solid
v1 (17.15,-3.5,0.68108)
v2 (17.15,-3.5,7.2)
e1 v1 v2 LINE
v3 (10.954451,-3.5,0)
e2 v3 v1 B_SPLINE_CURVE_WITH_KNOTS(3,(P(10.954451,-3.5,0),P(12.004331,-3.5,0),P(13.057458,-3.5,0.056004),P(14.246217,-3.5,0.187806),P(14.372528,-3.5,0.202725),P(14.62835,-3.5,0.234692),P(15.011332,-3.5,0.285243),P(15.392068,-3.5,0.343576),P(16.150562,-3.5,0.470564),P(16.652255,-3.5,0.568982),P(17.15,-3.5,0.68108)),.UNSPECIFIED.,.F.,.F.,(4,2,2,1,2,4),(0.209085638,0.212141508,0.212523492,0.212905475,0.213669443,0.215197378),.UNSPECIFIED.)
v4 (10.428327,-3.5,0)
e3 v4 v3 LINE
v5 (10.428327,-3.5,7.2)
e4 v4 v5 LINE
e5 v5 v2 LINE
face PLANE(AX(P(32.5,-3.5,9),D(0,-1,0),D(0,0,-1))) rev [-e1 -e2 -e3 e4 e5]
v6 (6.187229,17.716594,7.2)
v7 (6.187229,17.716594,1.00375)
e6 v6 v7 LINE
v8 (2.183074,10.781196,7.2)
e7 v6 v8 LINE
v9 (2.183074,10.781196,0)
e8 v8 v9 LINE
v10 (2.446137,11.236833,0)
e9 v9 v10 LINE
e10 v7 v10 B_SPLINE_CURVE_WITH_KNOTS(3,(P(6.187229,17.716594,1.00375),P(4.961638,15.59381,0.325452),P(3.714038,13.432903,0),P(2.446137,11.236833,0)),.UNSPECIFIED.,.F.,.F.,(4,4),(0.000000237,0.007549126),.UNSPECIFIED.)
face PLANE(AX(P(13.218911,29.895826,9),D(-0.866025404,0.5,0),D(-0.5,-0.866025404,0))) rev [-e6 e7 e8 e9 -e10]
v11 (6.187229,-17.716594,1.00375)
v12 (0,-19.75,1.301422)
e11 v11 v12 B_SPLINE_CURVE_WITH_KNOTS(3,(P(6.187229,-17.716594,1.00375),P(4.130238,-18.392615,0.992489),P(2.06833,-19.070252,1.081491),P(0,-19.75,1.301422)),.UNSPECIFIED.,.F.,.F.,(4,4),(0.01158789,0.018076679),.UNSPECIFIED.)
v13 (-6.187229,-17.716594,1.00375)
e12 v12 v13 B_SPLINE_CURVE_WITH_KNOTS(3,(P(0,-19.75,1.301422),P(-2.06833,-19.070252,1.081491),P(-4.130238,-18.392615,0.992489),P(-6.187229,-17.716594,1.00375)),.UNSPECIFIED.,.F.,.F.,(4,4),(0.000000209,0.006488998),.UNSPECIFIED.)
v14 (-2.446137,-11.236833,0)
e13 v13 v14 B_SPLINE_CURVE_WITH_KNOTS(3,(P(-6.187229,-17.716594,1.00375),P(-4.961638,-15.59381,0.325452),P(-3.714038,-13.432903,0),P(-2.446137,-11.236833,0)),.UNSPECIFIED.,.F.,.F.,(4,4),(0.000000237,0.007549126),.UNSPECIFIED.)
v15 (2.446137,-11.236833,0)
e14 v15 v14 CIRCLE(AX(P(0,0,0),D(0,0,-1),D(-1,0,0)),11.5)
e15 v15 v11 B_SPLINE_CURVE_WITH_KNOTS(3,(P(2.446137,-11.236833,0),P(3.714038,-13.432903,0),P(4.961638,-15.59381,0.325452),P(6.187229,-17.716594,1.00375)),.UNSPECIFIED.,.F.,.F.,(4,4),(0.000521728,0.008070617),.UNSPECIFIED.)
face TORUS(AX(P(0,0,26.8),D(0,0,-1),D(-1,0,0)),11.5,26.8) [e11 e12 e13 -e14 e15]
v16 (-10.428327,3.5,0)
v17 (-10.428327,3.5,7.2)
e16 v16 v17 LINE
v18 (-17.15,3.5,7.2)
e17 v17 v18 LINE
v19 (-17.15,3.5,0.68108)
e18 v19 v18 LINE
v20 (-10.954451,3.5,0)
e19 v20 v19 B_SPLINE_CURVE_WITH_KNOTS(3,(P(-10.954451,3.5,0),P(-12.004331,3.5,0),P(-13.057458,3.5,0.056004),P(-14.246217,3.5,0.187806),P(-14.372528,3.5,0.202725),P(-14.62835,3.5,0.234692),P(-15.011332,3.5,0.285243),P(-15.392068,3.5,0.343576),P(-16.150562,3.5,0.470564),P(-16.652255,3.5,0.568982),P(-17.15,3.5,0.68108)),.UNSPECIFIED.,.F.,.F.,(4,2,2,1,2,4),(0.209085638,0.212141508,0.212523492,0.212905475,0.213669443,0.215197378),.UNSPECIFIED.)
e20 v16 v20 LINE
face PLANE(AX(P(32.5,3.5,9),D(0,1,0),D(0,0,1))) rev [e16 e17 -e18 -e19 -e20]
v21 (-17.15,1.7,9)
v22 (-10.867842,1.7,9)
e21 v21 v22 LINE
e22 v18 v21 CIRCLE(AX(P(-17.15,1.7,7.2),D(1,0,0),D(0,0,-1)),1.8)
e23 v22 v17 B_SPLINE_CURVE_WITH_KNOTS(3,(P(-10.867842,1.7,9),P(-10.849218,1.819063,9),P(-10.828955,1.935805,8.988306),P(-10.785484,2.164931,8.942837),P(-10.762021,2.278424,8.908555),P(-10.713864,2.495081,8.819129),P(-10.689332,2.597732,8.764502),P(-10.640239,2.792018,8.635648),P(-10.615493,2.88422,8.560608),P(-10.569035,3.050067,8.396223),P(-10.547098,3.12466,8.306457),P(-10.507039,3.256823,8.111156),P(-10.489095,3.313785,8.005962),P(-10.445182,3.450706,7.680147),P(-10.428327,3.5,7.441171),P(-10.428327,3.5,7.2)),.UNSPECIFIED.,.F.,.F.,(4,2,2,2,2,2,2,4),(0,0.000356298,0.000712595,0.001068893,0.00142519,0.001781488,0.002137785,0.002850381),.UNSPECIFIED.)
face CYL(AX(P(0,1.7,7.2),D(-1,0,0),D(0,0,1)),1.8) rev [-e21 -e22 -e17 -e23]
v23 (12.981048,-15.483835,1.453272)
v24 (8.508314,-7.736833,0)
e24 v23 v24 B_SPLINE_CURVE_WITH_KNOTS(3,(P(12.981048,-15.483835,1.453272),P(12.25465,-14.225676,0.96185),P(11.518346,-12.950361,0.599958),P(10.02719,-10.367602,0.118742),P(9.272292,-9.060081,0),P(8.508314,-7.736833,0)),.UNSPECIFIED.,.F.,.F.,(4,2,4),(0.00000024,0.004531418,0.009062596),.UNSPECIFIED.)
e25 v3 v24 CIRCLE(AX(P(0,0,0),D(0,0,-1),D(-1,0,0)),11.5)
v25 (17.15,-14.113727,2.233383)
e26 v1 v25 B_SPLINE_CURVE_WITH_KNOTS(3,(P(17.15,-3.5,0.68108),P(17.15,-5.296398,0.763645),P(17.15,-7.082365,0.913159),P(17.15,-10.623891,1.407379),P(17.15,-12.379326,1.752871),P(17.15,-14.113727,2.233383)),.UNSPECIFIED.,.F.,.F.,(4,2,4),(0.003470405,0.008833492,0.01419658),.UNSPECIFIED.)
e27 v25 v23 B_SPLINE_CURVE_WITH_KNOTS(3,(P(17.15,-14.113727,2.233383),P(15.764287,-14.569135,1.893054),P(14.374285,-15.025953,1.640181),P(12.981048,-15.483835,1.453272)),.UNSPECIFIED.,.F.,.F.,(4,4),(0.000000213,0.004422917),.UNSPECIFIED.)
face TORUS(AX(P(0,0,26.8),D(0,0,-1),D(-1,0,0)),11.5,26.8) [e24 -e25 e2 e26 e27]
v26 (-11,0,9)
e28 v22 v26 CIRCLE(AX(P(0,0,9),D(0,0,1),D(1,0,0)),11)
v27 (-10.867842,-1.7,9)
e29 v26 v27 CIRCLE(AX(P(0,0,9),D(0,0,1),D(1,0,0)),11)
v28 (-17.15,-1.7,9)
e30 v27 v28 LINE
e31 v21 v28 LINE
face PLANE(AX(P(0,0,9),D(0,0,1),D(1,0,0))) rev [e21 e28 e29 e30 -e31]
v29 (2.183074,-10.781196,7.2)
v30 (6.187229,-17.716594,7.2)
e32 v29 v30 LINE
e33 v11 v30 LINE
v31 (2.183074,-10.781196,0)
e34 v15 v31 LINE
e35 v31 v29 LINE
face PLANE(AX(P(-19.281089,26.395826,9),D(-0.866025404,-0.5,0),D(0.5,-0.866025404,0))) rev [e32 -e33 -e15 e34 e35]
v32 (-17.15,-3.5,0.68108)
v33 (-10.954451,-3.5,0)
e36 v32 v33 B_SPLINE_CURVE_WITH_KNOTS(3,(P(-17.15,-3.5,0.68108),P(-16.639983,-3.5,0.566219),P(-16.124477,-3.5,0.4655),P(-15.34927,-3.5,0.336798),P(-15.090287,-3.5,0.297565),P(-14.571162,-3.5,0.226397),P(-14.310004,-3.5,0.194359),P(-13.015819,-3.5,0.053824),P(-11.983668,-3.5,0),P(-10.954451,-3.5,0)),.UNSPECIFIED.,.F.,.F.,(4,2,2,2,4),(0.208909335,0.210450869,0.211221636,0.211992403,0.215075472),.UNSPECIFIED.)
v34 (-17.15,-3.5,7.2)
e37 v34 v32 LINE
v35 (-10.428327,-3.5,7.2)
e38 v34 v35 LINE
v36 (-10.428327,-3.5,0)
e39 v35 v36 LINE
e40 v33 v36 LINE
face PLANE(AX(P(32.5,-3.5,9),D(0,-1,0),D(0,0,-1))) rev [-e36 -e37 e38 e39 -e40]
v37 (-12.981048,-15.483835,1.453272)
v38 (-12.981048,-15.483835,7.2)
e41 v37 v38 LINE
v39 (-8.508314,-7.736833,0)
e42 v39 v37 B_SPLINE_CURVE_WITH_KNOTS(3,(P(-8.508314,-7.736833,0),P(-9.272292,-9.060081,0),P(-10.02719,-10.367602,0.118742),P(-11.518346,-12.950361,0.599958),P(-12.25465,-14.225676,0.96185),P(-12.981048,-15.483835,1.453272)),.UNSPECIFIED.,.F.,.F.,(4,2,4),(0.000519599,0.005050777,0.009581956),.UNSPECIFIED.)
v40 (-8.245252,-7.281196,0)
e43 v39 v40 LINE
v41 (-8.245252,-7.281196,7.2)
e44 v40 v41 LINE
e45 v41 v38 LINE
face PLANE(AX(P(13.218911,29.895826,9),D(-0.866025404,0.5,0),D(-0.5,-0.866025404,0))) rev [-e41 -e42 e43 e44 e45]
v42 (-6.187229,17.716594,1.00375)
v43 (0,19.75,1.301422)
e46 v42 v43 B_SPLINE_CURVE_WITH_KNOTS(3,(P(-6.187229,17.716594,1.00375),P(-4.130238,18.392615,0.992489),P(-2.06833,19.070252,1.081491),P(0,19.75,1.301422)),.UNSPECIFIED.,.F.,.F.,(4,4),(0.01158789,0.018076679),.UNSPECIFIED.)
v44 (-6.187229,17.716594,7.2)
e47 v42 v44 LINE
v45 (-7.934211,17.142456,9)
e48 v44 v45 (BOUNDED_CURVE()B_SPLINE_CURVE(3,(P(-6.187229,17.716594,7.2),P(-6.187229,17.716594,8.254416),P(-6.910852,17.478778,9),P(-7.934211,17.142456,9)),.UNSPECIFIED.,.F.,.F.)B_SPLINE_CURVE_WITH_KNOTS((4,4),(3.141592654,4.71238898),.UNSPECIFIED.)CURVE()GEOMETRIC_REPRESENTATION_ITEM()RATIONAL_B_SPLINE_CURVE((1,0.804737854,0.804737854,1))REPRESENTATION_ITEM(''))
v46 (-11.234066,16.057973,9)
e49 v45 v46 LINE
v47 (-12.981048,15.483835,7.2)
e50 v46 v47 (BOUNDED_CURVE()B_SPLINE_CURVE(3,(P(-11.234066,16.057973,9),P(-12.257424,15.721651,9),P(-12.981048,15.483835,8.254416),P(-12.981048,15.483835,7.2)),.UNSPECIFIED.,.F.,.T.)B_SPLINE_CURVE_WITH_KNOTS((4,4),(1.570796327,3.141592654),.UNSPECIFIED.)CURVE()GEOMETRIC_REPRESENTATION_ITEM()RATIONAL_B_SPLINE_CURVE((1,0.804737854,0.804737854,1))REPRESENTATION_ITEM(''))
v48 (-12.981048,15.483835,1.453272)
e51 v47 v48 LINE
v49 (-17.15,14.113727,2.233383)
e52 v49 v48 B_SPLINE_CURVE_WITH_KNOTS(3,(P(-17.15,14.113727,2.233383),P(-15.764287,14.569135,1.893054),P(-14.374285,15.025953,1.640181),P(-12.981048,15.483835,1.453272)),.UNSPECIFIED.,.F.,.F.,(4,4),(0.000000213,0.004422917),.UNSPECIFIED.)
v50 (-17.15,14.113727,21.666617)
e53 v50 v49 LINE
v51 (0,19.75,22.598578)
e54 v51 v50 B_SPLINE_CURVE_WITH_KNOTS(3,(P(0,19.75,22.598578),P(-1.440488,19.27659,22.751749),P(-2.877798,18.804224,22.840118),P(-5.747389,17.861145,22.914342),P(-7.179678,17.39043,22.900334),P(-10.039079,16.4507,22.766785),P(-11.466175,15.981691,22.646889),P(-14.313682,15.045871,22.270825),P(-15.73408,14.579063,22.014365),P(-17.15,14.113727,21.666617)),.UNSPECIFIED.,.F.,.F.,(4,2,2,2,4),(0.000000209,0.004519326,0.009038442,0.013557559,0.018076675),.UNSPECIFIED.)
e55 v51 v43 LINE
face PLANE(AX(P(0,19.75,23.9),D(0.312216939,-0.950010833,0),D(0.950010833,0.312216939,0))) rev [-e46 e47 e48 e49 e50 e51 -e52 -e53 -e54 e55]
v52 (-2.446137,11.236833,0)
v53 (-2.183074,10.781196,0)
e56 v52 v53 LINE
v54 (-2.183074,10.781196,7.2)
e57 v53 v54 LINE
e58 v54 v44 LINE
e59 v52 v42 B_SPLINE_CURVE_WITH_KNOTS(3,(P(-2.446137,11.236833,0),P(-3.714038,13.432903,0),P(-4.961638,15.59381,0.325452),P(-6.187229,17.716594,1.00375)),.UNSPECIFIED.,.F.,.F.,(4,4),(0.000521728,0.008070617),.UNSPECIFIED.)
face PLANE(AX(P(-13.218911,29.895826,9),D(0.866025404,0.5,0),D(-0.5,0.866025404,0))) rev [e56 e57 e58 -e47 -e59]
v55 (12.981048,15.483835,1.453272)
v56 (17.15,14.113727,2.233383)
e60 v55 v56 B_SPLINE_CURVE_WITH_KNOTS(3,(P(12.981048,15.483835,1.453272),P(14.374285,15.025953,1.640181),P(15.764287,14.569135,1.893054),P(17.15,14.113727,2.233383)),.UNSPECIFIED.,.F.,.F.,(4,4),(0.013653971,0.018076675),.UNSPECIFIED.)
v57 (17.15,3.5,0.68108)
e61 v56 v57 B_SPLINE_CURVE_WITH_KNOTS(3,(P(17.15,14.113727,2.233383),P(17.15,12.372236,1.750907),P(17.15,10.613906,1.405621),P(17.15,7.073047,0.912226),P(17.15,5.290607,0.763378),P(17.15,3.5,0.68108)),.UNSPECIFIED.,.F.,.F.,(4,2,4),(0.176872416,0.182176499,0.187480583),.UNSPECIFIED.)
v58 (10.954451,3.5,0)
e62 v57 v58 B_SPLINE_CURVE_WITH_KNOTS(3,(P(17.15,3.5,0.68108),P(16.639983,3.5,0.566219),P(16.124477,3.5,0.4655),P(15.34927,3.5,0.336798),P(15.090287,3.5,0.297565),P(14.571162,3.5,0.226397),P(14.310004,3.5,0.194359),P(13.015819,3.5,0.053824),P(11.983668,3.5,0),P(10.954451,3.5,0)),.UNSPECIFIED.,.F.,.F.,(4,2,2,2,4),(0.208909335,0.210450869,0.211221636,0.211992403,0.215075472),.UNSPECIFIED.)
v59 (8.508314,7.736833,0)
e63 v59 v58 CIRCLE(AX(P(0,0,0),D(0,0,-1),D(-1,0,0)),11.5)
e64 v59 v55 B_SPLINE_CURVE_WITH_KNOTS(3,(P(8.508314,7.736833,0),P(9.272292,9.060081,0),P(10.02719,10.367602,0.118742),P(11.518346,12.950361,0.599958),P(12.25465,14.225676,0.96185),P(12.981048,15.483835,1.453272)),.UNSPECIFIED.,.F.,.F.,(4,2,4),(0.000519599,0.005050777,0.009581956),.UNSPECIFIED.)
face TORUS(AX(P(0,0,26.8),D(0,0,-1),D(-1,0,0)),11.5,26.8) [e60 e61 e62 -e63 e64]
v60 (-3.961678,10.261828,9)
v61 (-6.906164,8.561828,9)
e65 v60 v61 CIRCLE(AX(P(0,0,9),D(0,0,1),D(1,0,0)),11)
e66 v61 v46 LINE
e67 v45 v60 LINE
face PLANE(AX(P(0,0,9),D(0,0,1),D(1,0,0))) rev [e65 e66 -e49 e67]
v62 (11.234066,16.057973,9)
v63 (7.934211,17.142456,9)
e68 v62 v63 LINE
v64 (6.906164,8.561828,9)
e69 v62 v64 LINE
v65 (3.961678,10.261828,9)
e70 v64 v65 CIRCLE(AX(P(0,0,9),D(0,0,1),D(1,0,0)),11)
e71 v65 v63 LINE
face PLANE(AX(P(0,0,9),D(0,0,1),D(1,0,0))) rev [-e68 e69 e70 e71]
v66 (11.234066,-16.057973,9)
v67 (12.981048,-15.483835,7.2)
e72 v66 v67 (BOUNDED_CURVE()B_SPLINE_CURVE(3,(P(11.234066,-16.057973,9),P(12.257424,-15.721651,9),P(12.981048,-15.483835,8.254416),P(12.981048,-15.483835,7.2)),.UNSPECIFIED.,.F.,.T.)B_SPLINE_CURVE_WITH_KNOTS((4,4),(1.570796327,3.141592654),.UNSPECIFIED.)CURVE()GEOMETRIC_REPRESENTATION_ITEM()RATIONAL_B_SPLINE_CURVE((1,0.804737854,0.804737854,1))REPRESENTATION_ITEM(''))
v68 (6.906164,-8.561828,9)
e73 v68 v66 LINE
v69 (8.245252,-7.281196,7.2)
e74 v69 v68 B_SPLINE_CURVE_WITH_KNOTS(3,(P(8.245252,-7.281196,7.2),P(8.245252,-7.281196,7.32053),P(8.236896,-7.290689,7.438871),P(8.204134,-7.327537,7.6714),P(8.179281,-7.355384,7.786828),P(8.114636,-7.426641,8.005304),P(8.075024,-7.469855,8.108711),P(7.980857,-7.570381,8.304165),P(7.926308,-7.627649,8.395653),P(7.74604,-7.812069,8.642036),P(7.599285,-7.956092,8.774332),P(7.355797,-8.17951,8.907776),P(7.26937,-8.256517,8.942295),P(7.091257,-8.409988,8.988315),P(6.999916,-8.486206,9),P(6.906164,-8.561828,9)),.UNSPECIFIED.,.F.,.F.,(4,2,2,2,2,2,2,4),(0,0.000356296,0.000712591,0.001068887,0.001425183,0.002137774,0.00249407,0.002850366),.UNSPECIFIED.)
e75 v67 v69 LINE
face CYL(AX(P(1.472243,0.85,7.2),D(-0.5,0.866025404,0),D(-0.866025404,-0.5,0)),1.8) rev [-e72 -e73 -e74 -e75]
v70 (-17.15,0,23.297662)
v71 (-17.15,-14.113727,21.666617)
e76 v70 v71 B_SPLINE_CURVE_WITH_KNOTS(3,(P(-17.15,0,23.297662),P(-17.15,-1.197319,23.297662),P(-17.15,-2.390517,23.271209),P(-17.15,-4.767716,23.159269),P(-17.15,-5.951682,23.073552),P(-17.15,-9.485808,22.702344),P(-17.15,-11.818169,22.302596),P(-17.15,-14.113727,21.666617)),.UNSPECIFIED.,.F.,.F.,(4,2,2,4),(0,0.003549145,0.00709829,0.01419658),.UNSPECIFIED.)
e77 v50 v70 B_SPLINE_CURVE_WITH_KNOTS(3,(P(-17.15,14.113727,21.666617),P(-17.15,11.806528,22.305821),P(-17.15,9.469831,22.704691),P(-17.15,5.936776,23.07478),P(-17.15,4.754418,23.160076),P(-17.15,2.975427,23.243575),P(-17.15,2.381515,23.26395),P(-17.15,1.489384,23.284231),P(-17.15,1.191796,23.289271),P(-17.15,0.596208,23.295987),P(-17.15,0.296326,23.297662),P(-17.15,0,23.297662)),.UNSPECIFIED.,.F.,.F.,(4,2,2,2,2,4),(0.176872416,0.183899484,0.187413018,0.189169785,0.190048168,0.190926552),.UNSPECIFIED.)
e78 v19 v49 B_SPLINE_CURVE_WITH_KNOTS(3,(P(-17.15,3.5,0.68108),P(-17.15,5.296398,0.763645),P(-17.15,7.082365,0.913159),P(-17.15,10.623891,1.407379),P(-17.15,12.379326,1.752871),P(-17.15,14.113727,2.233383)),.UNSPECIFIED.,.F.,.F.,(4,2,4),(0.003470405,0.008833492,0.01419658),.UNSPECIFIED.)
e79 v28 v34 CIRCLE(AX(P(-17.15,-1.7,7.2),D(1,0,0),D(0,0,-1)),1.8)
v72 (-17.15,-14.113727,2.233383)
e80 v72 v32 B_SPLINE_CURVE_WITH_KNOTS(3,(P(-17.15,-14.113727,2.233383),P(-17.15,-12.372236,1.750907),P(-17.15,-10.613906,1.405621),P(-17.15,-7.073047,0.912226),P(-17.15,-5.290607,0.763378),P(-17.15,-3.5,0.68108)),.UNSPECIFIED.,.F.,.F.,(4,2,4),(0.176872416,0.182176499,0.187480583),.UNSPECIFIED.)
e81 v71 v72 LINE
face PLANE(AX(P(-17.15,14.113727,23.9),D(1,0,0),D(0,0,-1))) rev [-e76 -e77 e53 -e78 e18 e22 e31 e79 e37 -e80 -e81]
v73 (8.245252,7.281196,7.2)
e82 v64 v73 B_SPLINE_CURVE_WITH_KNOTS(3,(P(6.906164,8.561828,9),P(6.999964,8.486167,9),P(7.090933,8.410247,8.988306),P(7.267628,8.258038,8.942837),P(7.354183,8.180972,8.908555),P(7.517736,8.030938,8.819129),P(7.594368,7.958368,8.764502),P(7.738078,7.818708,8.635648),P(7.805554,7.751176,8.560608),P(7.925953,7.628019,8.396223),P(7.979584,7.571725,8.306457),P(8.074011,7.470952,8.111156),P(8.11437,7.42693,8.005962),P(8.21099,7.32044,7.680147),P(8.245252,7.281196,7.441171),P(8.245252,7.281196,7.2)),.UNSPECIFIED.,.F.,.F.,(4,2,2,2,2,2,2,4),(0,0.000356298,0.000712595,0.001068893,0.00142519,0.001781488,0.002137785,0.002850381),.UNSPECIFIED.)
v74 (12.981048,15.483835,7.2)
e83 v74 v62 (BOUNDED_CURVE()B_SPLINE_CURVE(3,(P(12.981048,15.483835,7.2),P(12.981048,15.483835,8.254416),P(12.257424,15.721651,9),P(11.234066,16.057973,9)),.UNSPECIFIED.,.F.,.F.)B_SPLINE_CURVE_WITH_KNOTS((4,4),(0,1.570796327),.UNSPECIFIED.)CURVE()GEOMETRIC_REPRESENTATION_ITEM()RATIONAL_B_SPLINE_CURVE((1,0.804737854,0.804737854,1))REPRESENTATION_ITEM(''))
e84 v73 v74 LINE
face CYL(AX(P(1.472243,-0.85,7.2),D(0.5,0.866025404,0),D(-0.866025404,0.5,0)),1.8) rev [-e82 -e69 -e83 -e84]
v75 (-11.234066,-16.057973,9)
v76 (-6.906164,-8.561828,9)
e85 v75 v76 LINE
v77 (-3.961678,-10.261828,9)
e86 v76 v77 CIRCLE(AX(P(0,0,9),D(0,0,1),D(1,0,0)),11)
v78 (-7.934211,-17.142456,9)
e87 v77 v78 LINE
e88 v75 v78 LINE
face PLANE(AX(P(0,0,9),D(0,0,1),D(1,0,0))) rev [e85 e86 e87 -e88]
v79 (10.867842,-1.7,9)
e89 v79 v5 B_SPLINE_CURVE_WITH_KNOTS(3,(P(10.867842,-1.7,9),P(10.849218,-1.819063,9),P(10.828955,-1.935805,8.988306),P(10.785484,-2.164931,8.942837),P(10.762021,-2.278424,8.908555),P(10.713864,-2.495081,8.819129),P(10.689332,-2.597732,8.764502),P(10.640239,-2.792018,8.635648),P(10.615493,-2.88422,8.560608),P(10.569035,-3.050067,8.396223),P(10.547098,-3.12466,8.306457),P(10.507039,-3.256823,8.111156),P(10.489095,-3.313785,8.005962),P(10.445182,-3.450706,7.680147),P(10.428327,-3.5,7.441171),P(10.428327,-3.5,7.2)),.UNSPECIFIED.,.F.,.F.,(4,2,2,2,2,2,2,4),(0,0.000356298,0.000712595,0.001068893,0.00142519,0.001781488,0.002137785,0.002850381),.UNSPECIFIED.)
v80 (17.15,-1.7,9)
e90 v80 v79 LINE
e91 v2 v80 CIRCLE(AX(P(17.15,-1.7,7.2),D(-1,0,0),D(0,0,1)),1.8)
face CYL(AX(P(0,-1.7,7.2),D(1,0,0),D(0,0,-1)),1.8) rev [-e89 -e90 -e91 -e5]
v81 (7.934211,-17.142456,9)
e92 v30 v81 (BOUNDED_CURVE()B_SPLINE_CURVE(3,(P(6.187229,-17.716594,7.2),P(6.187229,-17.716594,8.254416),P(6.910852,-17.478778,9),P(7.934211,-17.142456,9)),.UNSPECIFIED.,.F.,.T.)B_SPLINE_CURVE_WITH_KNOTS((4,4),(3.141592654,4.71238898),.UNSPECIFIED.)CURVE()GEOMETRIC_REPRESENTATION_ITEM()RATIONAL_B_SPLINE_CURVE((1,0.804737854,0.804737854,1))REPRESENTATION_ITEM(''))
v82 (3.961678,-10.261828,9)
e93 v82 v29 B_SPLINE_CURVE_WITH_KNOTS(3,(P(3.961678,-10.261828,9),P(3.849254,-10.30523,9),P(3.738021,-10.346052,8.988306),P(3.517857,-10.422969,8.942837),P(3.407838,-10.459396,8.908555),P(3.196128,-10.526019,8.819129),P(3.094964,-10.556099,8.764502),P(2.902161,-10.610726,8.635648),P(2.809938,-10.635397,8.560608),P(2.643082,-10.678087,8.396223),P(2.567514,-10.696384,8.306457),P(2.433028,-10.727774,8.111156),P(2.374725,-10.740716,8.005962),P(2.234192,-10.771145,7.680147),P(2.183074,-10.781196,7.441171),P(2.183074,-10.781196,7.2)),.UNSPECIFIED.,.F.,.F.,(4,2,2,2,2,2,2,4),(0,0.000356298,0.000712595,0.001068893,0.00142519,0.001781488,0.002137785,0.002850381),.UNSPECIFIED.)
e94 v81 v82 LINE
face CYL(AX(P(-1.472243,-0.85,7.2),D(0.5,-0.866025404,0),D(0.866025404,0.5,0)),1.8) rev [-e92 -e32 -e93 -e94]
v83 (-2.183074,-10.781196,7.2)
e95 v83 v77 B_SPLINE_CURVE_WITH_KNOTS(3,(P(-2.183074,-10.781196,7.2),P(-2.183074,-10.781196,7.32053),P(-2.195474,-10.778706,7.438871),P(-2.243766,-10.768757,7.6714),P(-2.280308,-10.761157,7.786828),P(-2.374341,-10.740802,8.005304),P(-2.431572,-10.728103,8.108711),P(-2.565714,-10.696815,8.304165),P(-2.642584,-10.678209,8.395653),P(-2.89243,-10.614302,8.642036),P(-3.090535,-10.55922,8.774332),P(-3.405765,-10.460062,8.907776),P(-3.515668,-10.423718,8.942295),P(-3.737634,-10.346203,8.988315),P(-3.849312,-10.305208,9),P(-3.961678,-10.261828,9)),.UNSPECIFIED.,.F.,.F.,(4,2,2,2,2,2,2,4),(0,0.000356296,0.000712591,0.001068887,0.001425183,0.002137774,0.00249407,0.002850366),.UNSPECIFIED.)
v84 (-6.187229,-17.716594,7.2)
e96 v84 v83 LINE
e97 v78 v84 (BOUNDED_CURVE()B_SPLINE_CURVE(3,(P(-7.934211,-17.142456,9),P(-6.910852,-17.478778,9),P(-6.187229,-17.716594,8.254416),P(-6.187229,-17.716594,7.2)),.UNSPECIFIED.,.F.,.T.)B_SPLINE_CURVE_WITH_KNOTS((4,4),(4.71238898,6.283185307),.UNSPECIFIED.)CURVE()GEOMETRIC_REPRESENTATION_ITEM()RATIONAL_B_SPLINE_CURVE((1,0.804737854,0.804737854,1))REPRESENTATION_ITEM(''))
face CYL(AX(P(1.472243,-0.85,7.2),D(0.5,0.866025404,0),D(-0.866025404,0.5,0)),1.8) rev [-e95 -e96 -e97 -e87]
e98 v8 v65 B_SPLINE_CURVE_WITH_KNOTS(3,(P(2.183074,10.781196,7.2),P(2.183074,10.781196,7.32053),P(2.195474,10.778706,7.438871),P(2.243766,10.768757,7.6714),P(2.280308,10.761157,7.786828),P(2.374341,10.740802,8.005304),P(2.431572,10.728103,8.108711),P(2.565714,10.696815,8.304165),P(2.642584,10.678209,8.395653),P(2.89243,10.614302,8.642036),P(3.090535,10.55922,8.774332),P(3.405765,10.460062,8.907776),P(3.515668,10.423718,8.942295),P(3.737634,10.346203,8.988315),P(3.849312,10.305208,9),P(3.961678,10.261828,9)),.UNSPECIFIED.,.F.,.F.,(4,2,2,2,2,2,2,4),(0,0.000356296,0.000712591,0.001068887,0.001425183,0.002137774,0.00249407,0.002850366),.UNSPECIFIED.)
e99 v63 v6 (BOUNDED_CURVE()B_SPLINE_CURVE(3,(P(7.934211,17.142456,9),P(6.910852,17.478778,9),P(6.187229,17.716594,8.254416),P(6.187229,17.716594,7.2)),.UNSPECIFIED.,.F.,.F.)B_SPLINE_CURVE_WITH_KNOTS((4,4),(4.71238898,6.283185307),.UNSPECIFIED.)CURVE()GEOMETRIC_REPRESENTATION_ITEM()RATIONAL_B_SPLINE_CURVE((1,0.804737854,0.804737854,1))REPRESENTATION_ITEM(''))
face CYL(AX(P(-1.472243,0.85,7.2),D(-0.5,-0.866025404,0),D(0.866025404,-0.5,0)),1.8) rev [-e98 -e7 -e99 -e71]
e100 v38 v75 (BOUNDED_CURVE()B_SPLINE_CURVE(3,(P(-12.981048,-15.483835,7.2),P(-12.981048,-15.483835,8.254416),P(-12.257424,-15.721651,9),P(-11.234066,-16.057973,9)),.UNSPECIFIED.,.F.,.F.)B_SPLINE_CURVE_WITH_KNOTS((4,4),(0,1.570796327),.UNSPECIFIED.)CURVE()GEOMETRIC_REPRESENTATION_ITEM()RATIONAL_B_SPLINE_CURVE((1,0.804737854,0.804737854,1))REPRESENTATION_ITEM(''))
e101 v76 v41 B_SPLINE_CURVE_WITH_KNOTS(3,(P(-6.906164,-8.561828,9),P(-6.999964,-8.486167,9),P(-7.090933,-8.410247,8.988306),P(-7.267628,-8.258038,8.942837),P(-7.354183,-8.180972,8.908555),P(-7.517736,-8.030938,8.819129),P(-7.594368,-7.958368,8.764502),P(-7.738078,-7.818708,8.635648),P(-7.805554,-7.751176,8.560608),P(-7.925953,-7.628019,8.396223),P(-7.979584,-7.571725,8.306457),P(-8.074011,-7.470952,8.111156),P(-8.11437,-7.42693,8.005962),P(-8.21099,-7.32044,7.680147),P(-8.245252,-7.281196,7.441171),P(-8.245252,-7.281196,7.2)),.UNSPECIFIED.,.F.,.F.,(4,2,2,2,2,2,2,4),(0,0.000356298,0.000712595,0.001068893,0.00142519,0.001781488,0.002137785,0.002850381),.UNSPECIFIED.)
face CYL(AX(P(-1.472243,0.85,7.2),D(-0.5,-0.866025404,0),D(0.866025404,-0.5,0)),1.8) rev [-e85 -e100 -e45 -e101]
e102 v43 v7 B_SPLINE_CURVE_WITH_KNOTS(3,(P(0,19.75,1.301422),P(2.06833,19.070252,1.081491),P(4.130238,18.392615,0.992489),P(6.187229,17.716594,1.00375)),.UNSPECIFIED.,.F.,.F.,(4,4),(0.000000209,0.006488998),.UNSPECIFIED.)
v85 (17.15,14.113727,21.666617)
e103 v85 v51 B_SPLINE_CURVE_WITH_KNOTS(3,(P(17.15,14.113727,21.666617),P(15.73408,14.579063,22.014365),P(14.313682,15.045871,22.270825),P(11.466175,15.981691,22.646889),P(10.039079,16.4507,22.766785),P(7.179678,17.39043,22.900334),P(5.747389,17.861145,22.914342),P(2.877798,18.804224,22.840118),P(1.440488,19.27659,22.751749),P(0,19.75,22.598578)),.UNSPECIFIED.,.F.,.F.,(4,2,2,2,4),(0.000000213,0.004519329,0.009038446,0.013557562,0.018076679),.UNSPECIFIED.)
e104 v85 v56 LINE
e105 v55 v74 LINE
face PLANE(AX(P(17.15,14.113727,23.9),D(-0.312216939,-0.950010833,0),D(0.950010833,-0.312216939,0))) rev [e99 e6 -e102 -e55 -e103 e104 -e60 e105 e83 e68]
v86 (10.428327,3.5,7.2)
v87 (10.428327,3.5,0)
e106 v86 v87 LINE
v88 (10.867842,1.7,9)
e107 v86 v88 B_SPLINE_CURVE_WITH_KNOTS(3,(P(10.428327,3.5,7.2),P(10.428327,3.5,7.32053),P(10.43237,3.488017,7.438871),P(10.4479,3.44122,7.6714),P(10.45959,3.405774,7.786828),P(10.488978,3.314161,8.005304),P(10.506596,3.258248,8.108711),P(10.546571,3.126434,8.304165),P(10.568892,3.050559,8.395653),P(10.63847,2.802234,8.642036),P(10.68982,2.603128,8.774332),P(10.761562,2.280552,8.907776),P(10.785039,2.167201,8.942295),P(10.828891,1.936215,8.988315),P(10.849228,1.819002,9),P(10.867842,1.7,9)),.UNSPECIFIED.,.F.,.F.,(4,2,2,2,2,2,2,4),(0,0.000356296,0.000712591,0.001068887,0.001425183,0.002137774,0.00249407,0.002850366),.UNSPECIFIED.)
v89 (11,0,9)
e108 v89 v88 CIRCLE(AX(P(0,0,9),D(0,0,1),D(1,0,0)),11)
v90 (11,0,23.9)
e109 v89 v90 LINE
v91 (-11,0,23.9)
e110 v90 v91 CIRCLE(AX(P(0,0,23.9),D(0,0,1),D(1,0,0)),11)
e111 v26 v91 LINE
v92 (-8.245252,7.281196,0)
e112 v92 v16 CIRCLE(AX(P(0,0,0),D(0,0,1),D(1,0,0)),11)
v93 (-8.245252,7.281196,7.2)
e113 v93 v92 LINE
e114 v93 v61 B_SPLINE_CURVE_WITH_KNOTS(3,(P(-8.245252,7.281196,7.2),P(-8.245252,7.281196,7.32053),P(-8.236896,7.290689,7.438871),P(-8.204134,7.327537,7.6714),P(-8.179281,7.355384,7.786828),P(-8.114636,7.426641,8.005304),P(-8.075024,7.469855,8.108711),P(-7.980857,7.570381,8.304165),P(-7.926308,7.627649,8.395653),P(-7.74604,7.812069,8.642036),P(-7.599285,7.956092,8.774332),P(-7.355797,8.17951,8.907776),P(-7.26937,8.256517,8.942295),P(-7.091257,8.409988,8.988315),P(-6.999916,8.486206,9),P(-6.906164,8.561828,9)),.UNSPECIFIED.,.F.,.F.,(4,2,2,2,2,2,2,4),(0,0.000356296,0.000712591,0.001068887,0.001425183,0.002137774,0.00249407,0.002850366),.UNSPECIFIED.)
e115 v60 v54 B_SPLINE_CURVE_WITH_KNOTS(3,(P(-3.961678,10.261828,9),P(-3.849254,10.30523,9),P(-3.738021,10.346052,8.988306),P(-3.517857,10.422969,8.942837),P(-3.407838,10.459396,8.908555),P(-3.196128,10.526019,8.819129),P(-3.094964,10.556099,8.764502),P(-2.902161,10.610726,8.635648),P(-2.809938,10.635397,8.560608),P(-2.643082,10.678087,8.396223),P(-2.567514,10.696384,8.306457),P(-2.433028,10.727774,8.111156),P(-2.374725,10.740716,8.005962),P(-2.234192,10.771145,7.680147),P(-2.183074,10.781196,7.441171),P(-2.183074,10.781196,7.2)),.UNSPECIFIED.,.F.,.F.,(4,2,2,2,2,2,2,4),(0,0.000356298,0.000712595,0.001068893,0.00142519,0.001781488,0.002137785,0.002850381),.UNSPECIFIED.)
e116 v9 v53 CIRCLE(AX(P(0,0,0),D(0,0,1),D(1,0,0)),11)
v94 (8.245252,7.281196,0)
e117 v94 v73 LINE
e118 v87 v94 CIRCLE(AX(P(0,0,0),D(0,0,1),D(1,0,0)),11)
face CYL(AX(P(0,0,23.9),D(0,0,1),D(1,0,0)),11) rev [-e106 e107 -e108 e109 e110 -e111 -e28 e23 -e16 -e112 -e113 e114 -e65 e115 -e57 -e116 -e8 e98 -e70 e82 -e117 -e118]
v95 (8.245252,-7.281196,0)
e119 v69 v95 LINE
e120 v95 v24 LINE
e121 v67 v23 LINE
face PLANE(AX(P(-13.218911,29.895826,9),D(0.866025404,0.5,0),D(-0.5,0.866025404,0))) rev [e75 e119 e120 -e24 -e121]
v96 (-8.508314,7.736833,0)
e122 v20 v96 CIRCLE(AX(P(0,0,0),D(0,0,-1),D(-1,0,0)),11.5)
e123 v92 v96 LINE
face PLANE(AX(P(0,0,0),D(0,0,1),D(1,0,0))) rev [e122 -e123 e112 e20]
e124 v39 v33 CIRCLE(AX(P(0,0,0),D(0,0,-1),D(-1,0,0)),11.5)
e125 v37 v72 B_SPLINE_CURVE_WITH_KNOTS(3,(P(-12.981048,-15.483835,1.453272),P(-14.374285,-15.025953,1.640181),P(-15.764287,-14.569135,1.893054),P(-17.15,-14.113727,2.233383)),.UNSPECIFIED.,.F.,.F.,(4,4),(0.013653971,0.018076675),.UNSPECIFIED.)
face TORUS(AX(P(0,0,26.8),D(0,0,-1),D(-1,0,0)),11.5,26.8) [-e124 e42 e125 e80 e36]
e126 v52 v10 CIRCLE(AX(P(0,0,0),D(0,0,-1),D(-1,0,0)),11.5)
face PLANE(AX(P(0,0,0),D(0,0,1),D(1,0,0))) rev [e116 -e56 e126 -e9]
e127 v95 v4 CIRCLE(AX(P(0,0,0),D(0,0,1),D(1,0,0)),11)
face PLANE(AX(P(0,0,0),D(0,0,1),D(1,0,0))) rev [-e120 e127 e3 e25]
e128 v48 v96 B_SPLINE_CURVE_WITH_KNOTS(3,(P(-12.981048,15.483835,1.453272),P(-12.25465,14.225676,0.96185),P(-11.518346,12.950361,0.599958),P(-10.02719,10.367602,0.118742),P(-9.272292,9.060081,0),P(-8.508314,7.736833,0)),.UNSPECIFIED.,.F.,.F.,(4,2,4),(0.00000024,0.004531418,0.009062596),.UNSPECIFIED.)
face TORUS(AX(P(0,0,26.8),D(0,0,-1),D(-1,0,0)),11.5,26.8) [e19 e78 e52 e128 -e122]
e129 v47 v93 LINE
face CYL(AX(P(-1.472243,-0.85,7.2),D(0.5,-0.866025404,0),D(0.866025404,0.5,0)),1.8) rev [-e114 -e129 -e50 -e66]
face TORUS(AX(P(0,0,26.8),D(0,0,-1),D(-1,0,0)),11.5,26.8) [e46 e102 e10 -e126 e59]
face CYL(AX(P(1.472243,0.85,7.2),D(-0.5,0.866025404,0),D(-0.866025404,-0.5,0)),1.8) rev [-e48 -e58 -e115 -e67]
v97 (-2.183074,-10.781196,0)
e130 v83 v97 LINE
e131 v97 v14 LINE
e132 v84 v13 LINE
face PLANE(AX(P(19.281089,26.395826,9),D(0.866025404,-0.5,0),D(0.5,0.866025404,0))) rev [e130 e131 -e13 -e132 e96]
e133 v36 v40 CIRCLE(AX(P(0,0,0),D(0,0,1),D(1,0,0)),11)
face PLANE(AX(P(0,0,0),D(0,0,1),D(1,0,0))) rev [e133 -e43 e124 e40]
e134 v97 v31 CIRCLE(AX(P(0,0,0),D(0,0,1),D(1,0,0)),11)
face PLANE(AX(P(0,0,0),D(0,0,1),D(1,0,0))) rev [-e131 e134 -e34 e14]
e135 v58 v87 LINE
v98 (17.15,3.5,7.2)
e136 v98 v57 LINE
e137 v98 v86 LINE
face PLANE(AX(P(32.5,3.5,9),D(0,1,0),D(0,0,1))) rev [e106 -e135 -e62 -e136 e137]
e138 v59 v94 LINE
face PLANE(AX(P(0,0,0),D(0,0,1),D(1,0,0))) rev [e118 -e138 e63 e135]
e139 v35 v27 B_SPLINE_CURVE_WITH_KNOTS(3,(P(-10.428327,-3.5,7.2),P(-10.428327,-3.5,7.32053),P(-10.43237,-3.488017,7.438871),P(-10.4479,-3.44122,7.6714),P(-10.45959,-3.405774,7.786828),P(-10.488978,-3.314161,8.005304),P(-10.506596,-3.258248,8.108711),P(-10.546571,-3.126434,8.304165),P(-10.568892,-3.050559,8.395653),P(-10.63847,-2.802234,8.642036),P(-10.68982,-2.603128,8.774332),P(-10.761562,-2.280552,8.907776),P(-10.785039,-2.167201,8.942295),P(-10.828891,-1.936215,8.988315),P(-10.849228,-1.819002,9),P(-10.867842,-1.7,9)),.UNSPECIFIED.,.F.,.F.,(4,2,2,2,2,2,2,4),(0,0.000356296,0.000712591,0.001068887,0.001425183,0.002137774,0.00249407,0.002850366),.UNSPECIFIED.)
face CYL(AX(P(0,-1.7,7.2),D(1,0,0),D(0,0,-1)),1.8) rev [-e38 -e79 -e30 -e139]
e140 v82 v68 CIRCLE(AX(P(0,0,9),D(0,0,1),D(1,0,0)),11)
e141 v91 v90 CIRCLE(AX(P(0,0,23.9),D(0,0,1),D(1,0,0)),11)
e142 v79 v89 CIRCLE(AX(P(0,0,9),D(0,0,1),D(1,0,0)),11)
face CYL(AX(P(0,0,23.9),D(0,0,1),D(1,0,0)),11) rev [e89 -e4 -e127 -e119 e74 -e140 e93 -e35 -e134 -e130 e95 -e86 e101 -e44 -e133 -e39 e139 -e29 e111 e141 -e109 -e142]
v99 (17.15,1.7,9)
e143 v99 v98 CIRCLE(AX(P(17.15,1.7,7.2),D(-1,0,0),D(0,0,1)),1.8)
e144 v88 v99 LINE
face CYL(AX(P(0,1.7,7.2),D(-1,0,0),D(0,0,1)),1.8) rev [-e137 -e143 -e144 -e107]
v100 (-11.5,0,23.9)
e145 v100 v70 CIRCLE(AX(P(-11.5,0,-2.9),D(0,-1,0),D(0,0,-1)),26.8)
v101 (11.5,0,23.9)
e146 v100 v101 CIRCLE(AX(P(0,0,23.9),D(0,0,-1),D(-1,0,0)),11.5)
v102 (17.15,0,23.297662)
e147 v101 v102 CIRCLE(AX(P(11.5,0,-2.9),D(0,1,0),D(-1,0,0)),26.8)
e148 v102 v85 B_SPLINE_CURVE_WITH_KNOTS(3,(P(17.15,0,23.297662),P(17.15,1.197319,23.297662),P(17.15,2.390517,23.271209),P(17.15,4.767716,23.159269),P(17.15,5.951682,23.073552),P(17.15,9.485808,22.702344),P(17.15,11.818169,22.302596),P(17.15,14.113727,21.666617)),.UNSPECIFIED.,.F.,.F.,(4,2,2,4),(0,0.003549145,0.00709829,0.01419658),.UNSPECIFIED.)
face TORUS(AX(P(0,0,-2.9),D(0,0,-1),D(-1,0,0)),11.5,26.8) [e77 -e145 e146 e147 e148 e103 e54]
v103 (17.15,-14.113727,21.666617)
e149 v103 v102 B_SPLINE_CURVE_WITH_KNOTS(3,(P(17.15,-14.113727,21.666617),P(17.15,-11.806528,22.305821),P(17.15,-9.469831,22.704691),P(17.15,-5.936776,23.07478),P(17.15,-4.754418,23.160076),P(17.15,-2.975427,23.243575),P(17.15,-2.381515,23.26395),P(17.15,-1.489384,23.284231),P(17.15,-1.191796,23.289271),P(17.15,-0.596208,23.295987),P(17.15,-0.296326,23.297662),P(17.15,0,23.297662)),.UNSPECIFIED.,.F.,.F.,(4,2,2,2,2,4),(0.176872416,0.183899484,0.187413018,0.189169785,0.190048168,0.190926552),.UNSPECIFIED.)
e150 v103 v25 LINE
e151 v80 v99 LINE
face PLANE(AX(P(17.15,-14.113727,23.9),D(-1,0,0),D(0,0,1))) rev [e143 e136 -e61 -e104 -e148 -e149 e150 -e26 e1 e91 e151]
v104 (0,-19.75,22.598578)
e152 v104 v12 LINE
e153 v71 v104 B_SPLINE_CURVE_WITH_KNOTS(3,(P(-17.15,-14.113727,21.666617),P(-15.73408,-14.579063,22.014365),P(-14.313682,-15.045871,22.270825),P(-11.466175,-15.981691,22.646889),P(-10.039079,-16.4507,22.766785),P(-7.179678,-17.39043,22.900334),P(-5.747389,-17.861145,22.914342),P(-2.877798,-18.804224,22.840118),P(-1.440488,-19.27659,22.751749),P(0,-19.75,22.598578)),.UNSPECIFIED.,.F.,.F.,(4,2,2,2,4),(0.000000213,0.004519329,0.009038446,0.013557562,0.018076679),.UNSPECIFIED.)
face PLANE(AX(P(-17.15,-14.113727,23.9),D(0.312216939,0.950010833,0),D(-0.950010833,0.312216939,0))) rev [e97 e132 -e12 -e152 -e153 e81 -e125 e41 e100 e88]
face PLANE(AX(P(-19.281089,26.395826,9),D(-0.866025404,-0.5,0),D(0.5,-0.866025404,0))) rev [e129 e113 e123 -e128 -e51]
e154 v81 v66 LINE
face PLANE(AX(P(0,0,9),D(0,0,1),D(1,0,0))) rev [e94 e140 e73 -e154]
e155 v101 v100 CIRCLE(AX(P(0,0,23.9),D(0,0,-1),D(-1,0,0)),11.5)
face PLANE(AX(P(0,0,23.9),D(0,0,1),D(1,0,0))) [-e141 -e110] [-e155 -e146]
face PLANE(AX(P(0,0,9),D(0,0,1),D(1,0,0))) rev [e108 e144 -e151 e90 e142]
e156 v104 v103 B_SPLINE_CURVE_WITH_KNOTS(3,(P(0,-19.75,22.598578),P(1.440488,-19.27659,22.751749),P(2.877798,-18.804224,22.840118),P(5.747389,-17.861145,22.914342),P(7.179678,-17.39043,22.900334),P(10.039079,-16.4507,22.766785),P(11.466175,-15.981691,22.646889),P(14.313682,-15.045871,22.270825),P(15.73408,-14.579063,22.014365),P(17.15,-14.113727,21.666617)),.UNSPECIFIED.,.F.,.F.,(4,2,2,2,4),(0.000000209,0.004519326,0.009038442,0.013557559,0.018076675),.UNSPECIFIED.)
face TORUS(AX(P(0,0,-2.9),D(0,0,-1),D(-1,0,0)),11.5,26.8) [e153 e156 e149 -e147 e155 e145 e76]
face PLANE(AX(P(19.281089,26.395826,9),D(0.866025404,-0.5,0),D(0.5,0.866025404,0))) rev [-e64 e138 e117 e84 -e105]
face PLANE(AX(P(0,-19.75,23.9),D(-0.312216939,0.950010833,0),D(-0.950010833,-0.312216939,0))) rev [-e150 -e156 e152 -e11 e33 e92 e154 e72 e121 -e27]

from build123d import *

# Parameters (mm, degrees)
BOSS_EXTRUDE1_DEPTH    = 23.9
SKETCH3_W              = 65
SKETCH3_H              = 7
CUT_EXTRUDE1_DEPTH     = 9
CIRPATTERN1_COUNT      = 3
CIRPATTERN1_ANGLE      = 120
M24X2_0_TAPPED_HOLE1_D = 22
FILLET2_R              = 1.8


with BuildPart() as part:
    # Sketch1 → Boss-Extrude1 (new body)
    with BuildSketch(Plane.XY):
        Polygon((0, 19.75), (-17.15, 14.1137269), (-17.15, -14.1137269), (0, -19.75), (17.15, -14.1137269), (17.15, 14.1137269), align=None)
    extrude(amount=BOSS_EXTRUDE1_DEPTH)

    # Sketch3 → Cut-Extrude1 (cut)
    with BuildSketch(Plane(origin=(0, 0, 0), x_dir=(-1, 0, 0), z_dir=(0, 0, -1))):
        Rectangle(SKETCH3_W, SKETCH3_H)
    cut_extrude1 = extrude(amount=-CUT_EXTRUDE1_DEPTH, mode=Mode.SUBTRACT)

    # CirPattern1: Cut-Extrude1 ×3 about axis
    cirpattern1_axis = Axis((0, 0, 0), (0, 0, 1))
    for i in range(1, CIRPATTERN1_COUNT):
        add(cut_extrude1.rotate(cirpattern1_axis, i * CIRPATTERN1_ANGLE / (CIRPATTERN1_COUNT - 1)), mode=Mode.SUBTRACT)

    # M24x2.0 Tapped Hole1 (through all)
    with Locations(Plane.XY.offset(23.9)):
        with Locations((0, 0)):
            Hole(M24X2_0_TAPPED_HOLE1_D / 2)

    # Fillet2
    fillet2_edges = [part.edges().sort_by_distance(p)[0] for p in [
        (-10.613150211, 11.382515394, 9),
        (4.185151513, 14.248895058, 9),
        (-4.185151513, -14.248895058, 9),
        (10.613150211, -11.382515394, 9),
        (-13.789163404, -3.5, 9),
        (13.789163404, 3.5, 9),
        (-13.789163404, 3.5, 9),
        (13.789163404, -3.5, 9),
        (-4.185151513, 14.248895058, 9),
        (4.185151513, -14.248895058, 9),
        (10.613150211, 11.382515394, 9),
        (-10.613150211, -11.382515394, 9),
    ]]
    fillet(fillet2_edges, radius=FILLET2_R)

    # Sketch8 → Cut-Revolve1 (revolve, cut)
    with BuildSketch(Plane(origin=(0, 0, 0), x_dir=(1, 0, 0), z_dir=(0, 1, 0))):
        with BuildLine():
            Line((11.5, 0), (33.520524336, 0))
            Line((33.520524336, 0), (33.520524336, -11.524643769))
            ThreePointArc((33.520524336, -11.524643769), (23.926995876, -3.055321154), (11.5, 0))
        make_face()
        with BuildLine():
            Line((11.5, -23.9), (28.830221364, -23.9))
            Line((28.830221364, -23.9), (28.830221364, -17.542686406))
            ThreePointArc((28.830221364, -17.542686406), (20.729734675, -22.260524594), (11.5, -23.9))
        make_face()
    revolve(axis=Axis((0, 0, -1.73), (0, 0, 1)), mode=Mode.SUBTRACT)


solid = part.part
